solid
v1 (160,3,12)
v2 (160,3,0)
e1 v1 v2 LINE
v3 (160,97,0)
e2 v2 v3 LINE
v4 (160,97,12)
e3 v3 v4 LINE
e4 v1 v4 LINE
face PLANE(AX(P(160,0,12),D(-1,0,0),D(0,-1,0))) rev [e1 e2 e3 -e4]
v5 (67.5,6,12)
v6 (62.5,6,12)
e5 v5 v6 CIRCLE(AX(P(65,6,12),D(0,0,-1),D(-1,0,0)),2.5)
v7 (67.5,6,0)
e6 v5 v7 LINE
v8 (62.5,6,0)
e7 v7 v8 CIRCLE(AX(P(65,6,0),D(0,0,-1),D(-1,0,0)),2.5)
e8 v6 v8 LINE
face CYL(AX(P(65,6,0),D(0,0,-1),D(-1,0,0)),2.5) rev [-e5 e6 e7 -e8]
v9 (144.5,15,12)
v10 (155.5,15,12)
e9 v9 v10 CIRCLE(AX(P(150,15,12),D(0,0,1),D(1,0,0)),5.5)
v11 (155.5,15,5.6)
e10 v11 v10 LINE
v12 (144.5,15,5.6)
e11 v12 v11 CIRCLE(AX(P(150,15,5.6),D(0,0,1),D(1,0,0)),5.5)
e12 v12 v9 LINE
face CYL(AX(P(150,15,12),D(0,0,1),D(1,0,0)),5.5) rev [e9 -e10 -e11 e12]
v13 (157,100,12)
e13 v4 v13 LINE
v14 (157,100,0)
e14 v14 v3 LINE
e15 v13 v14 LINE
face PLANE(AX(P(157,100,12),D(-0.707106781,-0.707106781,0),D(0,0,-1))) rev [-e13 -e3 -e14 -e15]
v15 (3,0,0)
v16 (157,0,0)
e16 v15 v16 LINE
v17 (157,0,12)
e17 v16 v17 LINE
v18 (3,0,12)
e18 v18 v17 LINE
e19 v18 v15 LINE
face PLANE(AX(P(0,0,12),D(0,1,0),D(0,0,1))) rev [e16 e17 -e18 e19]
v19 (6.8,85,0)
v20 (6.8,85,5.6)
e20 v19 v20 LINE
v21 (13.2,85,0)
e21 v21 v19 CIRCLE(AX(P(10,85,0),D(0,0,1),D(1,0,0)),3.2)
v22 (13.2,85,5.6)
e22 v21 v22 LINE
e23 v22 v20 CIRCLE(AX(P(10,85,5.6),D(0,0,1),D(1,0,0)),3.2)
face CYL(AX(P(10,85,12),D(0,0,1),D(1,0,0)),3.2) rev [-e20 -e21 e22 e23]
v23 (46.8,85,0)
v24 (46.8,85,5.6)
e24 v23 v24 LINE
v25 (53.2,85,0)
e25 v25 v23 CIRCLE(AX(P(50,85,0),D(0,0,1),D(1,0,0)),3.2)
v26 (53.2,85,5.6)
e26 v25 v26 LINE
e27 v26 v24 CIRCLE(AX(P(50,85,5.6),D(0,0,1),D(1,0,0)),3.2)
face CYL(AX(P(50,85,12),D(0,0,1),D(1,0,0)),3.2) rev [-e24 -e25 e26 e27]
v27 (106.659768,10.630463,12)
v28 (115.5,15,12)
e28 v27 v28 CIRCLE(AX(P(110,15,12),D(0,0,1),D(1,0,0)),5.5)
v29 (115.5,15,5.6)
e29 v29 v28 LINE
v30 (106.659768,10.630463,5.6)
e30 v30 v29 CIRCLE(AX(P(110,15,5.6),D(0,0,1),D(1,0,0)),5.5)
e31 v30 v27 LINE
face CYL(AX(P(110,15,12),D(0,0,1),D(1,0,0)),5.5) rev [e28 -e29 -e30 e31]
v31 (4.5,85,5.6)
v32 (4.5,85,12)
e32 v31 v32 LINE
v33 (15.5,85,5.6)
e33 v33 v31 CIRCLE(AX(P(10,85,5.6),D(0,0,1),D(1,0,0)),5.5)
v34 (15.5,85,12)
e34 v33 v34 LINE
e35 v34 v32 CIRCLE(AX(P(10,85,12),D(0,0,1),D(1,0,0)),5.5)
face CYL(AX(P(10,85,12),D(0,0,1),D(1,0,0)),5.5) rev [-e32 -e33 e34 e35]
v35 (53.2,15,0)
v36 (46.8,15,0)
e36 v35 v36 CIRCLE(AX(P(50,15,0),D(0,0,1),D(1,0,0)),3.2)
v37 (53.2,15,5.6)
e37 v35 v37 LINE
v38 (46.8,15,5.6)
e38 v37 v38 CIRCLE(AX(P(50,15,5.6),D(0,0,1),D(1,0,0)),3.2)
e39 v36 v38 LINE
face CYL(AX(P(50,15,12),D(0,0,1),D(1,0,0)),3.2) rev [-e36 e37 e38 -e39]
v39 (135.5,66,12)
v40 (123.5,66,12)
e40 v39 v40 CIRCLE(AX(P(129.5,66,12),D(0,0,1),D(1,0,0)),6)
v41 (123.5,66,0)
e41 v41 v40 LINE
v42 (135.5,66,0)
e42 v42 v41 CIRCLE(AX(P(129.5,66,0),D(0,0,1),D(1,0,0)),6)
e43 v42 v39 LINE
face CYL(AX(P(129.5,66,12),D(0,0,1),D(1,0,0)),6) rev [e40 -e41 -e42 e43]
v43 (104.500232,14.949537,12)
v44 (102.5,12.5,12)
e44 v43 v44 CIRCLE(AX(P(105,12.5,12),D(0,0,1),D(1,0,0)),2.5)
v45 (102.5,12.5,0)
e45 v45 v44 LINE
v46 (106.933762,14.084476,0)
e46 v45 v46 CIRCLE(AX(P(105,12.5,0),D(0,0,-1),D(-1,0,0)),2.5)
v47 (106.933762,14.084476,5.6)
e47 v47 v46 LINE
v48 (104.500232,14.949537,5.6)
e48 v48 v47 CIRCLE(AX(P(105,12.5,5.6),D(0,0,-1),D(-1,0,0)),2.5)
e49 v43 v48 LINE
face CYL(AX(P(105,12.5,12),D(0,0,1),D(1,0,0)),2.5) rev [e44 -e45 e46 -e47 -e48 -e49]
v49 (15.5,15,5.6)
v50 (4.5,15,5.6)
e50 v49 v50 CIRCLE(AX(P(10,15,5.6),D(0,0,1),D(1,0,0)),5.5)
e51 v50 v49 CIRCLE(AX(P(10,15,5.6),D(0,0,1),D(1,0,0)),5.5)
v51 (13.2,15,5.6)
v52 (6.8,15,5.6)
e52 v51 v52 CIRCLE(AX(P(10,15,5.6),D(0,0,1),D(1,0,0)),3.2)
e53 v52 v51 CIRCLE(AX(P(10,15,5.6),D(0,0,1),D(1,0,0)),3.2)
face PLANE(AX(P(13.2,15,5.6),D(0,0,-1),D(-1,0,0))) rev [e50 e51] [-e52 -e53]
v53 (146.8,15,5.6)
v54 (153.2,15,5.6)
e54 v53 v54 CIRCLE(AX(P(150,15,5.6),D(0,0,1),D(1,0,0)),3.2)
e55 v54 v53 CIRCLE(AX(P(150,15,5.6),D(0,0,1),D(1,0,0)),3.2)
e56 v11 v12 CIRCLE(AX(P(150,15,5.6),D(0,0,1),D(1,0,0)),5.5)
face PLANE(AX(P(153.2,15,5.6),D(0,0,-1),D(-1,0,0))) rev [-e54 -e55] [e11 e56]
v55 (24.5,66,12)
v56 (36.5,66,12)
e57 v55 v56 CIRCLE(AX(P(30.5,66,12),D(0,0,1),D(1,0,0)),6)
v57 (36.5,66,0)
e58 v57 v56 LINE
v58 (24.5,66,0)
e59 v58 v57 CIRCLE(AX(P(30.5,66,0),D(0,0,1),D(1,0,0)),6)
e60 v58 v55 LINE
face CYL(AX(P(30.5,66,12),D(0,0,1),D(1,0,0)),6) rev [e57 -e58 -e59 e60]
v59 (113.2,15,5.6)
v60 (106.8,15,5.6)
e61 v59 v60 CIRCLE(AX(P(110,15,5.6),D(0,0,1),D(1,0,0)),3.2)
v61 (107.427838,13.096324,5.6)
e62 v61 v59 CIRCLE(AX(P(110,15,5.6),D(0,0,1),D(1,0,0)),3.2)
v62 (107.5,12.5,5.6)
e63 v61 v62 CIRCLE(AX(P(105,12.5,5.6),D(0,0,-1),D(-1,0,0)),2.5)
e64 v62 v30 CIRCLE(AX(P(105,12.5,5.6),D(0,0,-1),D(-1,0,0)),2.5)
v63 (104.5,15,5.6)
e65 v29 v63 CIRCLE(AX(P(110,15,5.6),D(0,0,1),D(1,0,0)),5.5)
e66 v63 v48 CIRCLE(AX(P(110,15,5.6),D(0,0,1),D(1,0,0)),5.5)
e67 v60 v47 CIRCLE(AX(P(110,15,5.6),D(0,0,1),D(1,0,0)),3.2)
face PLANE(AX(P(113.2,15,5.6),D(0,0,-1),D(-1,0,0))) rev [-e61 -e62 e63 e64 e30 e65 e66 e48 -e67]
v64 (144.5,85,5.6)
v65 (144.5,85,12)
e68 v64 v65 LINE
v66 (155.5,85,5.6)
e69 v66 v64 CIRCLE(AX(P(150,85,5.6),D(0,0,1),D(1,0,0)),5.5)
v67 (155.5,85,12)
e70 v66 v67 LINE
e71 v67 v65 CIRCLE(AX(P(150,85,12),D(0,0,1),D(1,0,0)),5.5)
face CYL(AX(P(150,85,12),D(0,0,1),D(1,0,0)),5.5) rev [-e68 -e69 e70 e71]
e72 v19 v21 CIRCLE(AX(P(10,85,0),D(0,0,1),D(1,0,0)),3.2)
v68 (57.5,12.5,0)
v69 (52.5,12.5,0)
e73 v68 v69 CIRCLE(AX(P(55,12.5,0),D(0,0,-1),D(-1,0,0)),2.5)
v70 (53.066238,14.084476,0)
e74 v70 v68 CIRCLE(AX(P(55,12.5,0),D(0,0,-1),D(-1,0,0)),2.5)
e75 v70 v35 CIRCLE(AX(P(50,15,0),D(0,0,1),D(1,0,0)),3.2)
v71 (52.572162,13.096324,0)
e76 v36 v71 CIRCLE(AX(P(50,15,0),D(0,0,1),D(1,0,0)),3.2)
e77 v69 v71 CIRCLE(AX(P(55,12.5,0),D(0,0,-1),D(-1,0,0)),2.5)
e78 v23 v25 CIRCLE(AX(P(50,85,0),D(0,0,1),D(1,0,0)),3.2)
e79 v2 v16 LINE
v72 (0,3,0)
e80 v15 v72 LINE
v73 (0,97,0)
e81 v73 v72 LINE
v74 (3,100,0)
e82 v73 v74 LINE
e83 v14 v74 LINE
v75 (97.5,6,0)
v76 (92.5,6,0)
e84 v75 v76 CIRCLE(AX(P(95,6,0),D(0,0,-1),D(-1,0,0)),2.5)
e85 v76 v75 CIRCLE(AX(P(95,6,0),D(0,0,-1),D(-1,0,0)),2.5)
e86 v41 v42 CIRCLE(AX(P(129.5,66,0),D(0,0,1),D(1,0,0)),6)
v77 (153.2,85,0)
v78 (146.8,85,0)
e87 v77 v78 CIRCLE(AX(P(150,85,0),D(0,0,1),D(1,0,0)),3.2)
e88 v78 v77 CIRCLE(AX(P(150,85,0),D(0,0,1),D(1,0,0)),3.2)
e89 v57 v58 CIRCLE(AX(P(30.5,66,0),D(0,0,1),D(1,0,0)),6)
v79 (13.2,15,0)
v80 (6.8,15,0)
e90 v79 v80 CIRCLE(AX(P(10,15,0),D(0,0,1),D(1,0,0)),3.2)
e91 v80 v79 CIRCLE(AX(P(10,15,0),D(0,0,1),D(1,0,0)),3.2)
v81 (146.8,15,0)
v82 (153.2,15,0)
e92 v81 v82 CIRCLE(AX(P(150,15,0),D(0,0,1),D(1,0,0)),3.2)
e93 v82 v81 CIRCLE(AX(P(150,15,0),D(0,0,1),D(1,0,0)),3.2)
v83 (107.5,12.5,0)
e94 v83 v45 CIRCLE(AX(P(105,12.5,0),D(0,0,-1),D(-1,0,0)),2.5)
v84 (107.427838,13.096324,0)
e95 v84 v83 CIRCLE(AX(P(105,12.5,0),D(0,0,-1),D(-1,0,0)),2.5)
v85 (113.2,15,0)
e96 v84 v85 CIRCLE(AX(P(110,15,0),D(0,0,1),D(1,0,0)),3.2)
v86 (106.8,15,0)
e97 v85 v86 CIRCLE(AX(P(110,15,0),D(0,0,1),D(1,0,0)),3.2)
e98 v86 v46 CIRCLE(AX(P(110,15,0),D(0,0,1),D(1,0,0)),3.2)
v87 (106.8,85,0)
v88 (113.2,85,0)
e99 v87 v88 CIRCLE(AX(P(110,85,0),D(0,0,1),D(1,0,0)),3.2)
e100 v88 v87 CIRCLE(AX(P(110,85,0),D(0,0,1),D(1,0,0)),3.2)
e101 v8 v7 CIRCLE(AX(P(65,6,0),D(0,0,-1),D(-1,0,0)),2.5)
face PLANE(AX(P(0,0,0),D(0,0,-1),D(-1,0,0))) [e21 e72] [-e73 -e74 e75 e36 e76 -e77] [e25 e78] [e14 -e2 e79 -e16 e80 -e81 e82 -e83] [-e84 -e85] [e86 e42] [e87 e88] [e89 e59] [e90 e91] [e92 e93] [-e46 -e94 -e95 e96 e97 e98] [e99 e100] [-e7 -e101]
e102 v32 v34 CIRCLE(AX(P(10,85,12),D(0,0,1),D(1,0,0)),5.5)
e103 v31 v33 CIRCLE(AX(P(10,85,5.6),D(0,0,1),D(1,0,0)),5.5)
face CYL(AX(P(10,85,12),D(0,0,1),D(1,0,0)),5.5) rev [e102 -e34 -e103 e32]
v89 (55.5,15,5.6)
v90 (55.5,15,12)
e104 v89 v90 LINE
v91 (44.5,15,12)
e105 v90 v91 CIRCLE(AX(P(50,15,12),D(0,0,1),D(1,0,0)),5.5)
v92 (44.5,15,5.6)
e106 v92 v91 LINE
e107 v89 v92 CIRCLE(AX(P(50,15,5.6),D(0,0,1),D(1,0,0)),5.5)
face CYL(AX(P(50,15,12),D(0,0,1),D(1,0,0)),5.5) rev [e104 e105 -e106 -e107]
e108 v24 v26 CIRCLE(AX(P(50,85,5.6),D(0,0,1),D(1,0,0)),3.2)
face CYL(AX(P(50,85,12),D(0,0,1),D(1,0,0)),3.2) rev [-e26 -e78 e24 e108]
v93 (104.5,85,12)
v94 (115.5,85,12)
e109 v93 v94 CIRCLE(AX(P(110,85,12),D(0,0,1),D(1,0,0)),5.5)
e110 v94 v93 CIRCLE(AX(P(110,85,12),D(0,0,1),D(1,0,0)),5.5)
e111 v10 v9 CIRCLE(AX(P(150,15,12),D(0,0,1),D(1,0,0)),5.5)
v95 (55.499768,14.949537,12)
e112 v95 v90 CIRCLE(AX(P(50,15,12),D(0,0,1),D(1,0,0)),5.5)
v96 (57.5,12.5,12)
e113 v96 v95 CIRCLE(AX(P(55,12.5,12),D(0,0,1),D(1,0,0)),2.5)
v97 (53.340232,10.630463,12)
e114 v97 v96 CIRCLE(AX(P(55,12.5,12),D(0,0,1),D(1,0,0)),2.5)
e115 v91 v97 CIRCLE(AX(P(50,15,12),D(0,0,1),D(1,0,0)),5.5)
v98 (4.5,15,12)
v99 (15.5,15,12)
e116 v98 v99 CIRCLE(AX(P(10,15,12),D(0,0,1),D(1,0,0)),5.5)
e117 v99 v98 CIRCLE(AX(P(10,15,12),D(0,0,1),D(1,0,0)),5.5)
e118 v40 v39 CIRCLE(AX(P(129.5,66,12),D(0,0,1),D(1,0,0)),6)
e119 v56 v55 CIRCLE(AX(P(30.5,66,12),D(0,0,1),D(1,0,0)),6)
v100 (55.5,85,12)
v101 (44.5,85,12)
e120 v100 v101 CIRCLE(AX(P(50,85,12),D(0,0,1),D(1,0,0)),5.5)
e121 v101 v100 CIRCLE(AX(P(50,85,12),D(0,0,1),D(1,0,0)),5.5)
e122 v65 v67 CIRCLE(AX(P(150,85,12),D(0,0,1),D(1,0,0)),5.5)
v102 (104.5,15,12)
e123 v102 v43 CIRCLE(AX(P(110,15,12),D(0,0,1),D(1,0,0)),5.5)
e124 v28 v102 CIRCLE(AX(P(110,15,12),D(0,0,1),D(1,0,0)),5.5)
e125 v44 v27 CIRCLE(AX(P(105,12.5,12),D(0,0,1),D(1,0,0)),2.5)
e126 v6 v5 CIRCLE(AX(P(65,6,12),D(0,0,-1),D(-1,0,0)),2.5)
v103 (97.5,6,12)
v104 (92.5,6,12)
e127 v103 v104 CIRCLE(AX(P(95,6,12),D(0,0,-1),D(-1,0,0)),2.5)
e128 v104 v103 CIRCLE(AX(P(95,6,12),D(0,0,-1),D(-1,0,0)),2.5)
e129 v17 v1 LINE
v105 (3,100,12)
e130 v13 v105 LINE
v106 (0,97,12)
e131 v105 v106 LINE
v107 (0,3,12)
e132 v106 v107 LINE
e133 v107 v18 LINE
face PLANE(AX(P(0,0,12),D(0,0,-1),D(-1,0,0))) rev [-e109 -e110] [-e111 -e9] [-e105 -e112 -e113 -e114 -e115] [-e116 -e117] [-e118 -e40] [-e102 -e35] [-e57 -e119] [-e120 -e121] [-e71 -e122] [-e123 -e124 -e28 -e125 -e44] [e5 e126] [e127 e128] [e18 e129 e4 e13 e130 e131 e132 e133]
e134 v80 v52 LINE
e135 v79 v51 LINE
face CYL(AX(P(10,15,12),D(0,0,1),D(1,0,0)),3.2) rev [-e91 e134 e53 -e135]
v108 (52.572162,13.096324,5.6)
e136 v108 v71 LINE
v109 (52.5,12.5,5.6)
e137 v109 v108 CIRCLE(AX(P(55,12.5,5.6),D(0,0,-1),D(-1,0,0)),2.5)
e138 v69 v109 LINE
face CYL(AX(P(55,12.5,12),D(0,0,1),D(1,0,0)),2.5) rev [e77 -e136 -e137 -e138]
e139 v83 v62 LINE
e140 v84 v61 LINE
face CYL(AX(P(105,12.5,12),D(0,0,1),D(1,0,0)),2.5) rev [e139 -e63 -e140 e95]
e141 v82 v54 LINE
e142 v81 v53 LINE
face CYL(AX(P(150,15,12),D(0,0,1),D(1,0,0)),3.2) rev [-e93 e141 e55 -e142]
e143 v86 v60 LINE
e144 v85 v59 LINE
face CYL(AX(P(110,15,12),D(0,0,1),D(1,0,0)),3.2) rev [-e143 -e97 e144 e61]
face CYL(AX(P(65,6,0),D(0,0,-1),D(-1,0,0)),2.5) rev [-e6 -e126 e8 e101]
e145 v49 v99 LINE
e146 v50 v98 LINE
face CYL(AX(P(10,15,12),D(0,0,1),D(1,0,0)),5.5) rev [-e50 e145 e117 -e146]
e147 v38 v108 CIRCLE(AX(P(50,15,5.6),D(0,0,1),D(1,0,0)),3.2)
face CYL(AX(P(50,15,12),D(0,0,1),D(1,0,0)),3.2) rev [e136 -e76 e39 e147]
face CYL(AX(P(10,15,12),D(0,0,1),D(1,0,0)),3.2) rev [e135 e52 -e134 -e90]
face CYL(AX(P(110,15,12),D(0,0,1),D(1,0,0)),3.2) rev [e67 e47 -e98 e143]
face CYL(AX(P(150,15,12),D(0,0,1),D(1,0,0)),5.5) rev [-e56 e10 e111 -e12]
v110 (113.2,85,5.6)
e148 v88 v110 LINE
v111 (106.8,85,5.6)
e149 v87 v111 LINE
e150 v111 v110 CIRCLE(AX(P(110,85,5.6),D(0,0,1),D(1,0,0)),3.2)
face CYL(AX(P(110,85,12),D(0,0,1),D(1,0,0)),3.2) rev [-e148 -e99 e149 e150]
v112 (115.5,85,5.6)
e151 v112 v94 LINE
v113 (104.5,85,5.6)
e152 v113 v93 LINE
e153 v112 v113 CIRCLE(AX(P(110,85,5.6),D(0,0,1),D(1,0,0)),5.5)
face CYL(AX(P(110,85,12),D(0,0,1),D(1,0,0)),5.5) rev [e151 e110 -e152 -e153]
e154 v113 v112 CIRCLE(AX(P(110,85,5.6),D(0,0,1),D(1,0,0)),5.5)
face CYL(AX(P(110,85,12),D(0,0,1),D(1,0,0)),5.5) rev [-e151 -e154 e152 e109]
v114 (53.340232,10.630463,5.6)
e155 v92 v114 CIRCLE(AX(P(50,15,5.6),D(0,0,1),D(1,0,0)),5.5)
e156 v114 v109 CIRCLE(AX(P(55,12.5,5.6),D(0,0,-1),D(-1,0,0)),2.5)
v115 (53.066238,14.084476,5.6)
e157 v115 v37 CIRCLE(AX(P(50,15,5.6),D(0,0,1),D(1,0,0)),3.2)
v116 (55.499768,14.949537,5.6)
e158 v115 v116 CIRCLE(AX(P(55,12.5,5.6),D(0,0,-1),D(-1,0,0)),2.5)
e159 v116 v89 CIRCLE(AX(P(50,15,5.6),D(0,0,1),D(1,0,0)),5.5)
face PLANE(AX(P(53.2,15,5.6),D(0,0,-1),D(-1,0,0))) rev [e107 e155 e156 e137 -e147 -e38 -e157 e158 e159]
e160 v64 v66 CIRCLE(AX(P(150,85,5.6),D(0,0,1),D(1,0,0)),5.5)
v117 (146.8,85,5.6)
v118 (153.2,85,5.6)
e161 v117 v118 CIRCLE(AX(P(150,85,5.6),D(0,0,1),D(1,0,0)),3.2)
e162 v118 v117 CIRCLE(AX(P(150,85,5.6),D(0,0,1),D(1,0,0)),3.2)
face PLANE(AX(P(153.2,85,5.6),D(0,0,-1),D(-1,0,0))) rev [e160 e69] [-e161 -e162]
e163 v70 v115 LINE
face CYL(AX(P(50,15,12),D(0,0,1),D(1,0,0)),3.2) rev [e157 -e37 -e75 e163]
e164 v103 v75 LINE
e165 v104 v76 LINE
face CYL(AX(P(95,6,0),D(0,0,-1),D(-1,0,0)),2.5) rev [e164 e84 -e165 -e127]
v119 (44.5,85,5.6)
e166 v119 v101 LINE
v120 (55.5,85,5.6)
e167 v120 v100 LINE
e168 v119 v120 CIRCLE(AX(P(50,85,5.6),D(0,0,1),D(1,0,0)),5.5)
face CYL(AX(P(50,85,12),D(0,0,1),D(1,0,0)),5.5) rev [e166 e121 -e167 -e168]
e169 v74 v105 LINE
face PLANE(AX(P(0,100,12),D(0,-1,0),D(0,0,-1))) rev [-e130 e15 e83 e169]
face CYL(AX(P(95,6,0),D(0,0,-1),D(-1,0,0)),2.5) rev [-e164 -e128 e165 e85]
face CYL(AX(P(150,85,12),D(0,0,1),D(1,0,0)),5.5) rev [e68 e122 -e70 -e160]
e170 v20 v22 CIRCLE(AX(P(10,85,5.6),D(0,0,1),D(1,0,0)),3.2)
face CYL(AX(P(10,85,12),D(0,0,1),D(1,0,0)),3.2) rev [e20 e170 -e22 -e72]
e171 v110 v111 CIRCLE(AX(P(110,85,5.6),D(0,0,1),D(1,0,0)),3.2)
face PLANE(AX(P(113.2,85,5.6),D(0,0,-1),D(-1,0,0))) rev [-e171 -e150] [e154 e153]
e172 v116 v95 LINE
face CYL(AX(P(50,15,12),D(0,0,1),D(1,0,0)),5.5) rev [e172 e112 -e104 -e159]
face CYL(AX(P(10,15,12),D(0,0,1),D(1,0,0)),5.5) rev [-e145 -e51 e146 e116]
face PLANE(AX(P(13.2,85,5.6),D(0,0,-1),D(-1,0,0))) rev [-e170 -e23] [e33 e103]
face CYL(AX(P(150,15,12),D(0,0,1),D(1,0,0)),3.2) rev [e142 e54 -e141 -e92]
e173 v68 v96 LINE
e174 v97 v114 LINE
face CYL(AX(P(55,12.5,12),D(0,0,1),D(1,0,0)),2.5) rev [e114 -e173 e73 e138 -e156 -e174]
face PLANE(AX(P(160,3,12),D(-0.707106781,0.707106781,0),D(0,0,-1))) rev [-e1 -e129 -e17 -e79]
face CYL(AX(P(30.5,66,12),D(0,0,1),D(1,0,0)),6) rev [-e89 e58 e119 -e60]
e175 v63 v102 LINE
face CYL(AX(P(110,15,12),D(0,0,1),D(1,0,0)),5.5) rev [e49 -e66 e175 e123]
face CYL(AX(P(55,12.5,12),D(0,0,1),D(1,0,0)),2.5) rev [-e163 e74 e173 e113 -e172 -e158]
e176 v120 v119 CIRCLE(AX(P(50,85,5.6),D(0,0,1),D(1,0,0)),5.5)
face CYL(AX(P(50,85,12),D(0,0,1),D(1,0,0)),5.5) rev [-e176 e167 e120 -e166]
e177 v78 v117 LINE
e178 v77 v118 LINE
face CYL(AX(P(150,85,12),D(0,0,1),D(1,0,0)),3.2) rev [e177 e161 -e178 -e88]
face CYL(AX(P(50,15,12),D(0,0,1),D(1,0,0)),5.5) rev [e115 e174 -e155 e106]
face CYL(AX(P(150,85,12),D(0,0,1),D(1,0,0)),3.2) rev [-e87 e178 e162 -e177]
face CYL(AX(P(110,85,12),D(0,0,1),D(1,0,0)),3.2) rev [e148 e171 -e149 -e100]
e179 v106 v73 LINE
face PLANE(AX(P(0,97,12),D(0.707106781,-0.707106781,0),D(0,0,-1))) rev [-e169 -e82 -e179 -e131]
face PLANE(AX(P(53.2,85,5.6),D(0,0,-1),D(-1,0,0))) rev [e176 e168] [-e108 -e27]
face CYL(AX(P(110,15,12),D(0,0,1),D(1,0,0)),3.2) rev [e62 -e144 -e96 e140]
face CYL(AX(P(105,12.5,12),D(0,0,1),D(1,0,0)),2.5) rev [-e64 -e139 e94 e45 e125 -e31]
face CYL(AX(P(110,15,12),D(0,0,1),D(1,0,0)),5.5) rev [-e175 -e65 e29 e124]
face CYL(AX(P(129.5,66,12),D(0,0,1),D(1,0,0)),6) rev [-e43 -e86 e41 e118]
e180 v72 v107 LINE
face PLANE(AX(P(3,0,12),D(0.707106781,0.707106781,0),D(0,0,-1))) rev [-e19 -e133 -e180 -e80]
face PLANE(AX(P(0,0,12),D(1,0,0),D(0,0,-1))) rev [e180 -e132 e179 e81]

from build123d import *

# Parameters (mm, degrees)
SKETCH_1_W                   = 160
SKETCH_1_H                   = 100
EXTRUDE_1_DEPTH              = 12
HOLE_WIZARD_M14_1_D          = 12
HOLE_WIZARD_M6_1_D           = 6.4
HOLE_WIZARD_M6_1_CBORE_D     = 11
HOLE_WIZARD_M6_1_CBORE_DEPTH = 6.4
CHAMFER_1_SIZE               = 3
HOLE_WIZARD_M6_1_2_D         = 5
HOLE_WIZARD_M6_2_D           = 5
HOLE_WIZARD_M6_2_DEPTH       = 15
HOLE_WIZARD_M6_2_TIP         = 1.502151548


with BuildPart() as part:
    # 草图1 → 凸台-拉伸1 (new body)
    with BuildSketch(Plane.XY):
        with Locations((80, 50)):
            Rectangle(SKETCH_1_W, SKETCH_1_H)
    extrude(amount=EXTRUDE_1_DEPTH)

    # M14 螺纹孔1 (through all)
    with Locations(Plane.XY.offset(12)):
        with Locations((30.5, 66), (129.5, 66)):
            Hole(HOLE_WIZARD_M14_1_D / 2)

    # Hole Wizard M6 _1 (through all)
    with Locations(Plane.XY.offset(12)):
        with Locations((10, 15), (50, 15), (50, 85), (10, 85), (110, 15), (150, 15), (150, 85), (110, 85)):
            CounterBoreHole(HOLE_WIZARD_M6_1_D / 2, HOLE_WIZARD_M6_1_CBORE_D / 2, HOLE_WIZARD_M6_1_CBORE_DEPTH)

    # 倒角1
    chamfer_1_edges = [part.edges().sort_by_distance(p)[0] for p in [
        (0, 100, 6),
        (160, 100, 6),
        (160, 0, 6),
        (0, 0, 6),
    ]]
    chamfer(chamfer_1_edges, length=CHAMFER_1_SIZE)

    # Hole Wizard M6 _1 2 (through all)
    with Locations(Plane(origin=(0, 0, 0), x_dir=(-1, 0, 0), z_dir=(0, 0, -1))):
        with Locations((-65, 6), (-95, 6)):
            Hole(HOLE_WIZARD_M6_1_2_D / 2)

    # M6 螺纹孔2
    with Locations(Plane.XY.offset(12)):
        with Locations((55, 12.5), (105, 12.5)):
            Hole(HOLE_WIZARD_M6_2_D / 2, depth=HOLE_WIZARD_M6_2_DEPTH)
            with Locations((0, 0, -(HOLE_WIZARD_M6_2_DEPTH + HOLE_WIZARD_M6_2_TIP / 2))):  # 118° drill point
                Cone(0, HOLE_WIZARD_M6_2_D / 2, HOLE_WIZARD_M6_2_TIP, mode=Mode.SUBTRACT)


solid = part.part
